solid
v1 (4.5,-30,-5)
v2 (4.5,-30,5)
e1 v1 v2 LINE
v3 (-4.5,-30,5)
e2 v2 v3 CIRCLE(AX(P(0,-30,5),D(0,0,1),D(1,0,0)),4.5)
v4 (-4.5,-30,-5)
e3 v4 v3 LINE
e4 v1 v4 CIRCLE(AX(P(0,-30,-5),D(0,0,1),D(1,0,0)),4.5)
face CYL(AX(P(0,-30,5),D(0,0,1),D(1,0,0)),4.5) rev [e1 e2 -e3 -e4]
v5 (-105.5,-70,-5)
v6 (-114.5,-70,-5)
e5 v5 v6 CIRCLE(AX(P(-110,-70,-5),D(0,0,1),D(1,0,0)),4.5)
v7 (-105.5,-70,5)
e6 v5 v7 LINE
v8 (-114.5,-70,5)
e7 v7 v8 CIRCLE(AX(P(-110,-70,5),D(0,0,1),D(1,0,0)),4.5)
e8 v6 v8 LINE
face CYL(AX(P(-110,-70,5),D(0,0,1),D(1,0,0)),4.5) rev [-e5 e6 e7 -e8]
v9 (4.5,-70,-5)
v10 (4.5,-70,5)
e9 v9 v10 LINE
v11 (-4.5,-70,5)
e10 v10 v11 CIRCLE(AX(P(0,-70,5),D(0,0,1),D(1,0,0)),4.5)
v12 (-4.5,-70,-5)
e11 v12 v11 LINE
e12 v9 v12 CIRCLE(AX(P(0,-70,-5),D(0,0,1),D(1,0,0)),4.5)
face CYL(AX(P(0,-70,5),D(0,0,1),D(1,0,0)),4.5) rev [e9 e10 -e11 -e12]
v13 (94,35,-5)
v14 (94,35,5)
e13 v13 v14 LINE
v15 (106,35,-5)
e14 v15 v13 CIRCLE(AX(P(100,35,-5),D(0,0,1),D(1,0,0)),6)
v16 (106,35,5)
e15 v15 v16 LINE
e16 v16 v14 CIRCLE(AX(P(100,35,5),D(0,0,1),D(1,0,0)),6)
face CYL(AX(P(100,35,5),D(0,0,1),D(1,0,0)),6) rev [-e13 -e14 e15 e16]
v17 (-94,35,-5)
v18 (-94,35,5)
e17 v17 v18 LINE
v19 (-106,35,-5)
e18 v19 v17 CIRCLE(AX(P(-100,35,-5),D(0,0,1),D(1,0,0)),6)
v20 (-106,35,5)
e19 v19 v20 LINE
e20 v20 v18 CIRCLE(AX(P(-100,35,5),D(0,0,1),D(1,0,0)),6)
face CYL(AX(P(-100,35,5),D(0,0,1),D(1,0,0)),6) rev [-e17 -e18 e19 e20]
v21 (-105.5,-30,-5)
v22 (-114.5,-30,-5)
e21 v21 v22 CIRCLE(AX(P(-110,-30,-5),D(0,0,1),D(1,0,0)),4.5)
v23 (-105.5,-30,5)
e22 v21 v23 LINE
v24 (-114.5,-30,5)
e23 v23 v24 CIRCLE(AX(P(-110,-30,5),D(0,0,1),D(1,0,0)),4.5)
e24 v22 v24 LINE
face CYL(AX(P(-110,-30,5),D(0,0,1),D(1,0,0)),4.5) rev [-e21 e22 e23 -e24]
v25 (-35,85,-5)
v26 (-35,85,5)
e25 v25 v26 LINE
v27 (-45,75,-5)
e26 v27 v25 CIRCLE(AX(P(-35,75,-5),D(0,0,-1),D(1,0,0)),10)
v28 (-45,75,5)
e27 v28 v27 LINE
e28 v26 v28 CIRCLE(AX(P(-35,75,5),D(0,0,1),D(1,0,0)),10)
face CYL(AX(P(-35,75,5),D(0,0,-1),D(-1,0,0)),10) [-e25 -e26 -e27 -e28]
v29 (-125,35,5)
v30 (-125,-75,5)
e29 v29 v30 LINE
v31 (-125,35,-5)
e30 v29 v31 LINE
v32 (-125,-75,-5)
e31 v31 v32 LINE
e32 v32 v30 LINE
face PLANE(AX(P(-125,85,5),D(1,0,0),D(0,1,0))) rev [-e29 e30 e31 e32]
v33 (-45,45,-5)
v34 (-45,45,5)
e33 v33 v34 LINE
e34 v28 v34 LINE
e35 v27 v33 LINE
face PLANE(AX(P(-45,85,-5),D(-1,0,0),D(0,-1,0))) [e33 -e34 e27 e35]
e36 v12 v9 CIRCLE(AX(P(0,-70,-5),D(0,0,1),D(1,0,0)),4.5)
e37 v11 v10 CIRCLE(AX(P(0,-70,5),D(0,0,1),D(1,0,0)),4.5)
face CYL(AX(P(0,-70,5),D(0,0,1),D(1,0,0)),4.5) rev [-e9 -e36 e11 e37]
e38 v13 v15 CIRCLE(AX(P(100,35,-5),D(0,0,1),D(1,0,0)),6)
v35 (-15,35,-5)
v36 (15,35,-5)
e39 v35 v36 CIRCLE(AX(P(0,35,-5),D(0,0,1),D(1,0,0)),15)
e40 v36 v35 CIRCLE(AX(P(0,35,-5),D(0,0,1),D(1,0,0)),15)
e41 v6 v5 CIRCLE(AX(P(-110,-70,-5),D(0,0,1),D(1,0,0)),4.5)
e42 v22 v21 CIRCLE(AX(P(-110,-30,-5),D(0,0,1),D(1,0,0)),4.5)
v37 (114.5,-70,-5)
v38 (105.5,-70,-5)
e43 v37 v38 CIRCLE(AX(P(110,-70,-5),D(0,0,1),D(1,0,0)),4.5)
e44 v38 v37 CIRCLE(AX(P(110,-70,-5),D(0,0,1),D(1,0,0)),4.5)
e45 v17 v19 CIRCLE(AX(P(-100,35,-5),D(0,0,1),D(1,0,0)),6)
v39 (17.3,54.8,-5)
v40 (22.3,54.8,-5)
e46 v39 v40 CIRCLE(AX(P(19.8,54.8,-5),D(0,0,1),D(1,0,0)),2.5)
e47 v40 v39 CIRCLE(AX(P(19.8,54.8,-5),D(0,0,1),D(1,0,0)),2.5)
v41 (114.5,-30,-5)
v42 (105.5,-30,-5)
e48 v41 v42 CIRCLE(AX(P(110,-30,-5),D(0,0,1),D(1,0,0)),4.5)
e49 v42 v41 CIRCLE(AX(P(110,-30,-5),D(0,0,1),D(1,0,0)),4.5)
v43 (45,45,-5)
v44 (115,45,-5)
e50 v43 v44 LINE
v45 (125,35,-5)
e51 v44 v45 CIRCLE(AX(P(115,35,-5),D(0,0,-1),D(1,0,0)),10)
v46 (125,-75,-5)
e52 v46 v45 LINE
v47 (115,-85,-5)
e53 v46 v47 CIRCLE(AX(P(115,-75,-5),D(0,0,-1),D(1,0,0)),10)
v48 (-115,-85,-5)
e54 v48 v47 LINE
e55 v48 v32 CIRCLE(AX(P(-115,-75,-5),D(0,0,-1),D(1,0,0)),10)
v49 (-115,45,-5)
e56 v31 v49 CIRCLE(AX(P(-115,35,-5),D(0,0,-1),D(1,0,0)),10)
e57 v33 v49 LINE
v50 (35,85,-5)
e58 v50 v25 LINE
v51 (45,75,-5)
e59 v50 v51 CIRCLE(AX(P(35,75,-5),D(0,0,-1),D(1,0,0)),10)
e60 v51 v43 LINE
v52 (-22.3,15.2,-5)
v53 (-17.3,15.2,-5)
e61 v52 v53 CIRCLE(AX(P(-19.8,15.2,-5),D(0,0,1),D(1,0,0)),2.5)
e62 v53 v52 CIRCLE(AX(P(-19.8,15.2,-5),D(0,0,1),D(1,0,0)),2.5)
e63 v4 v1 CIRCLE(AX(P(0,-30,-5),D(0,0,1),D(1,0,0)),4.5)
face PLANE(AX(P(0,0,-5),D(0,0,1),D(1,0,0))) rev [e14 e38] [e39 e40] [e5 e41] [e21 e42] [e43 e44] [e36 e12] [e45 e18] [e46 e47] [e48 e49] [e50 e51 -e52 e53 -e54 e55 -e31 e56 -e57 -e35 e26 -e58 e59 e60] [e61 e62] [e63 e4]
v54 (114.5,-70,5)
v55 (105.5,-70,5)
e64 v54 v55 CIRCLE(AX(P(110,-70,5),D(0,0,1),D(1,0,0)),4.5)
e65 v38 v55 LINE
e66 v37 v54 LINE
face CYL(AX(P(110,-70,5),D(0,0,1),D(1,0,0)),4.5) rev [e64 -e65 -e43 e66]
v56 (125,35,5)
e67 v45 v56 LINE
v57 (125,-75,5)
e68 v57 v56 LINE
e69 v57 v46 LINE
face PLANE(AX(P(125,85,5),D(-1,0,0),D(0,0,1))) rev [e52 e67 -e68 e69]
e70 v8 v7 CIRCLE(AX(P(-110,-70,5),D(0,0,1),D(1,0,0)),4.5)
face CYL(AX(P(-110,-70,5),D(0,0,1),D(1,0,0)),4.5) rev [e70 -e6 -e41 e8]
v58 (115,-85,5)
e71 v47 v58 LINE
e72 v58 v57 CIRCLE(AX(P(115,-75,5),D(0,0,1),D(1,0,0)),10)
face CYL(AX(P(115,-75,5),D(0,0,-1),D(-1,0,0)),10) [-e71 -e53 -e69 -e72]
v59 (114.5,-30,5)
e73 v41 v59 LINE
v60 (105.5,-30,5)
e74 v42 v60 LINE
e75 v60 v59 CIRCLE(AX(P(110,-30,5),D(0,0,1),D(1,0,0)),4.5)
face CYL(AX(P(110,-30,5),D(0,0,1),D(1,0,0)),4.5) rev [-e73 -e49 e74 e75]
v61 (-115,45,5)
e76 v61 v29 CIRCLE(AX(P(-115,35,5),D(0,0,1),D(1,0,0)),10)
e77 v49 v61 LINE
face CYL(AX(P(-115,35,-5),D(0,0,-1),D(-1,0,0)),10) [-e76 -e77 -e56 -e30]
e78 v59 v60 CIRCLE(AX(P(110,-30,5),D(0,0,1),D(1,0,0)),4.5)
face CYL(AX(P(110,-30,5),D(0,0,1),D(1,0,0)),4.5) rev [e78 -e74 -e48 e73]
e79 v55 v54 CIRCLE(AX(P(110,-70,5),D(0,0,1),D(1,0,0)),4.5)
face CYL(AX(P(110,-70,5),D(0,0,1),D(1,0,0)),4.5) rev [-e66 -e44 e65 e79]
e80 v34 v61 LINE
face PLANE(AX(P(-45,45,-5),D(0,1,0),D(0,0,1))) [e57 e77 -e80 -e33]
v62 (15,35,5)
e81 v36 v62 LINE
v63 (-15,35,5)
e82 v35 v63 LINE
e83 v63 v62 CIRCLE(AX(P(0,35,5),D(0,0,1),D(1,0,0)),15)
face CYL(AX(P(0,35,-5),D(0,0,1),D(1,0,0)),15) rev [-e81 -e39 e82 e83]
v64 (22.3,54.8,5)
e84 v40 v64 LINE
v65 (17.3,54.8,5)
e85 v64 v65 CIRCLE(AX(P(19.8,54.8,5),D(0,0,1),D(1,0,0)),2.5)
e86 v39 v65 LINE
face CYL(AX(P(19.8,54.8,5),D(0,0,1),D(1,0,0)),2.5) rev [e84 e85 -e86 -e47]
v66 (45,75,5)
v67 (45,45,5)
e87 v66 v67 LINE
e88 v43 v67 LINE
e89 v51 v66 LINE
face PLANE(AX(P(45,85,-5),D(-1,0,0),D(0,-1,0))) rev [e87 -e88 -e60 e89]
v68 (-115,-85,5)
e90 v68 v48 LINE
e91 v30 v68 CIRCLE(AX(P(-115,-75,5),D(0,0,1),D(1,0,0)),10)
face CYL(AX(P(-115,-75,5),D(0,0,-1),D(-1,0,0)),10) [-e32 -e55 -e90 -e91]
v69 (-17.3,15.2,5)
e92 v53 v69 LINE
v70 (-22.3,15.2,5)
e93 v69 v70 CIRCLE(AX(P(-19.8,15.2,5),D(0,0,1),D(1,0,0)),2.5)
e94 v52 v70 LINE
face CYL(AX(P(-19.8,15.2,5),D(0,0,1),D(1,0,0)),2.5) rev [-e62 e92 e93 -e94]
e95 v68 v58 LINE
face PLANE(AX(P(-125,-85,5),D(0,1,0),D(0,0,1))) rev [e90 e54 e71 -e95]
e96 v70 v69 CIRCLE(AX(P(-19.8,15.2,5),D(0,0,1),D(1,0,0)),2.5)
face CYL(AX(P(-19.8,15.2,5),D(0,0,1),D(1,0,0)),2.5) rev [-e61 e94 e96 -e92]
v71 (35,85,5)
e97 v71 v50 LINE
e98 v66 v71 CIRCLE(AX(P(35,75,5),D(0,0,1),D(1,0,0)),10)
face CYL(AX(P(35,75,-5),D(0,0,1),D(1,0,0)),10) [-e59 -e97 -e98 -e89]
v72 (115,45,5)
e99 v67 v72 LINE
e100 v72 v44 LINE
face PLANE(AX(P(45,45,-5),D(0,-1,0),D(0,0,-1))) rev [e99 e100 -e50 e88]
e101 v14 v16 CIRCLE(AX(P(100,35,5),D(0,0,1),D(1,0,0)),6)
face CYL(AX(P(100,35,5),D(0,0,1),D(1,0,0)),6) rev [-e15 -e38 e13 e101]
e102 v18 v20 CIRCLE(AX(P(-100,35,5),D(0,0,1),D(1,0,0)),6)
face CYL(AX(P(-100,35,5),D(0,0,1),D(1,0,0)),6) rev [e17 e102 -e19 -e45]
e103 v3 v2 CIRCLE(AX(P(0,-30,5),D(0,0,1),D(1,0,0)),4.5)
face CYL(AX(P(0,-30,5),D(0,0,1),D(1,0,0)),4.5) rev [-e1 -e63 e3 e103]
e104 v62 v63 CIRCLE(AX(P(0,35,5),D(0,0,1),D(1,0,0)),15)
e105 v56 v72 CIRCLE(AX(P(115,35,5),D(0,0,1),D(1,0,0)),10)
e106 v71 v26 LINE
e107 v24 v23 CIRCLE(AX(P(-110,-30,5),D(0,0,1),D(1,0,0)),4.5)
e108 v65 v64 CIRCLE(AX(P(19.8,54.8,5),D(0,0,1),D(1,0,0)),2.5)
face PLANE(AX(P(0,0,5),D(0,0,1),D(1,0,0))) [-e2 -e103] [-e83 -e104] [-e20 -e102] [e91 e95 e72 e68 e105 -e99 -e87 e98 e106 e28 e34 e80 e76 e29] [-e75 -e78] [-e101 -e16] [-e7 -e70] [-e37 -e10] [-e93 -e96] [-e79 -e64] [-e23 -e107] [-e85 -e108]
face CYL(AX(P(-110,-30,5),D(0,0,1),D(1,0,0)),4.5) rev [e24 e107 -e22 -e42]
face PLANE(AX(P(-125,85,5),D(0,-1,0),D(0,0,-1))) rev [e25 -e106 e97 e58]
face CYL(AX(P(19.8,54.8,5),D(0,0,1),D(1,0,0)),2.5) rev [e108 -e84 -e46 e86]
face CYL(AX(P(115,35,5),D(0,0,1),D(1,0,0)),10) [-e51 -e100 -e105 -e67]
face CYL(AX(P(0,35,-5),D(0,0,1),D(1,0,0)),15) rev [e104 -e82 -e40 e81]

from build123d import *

# Parameters (mm, degrees)
SKETCH_1_W              = 250
SKETCH_1_H              = 170
EXTRUDE_1_DEPTH         = 5
SKETCH_2_W              = 80
SKETCH_2_H              = 40
CUT_EXTRUDE_1_DEPTH     = 10
HOLE_WIZARD_9_0_9_1_D   = 9
PATTERN_LINEAR_1_COUNT  = 3
PATTERN_LINEAR_1_PITCH  = 110
HOLE_WIZARD_12_0_12_1_D = 12
SKETCH_7_R              = 15
CUT_EXTRUDE_2_DEPTH     = 10
HOLE_WIZARD_M6_1_D      = 5
FILLET_1_R              = 10


with BuildPart() as part:
    # 草图1 → 凸台-拉伸1 (new, symmetric)
    with BuildSketch(Plane.XY):
        Rectangle(SKETCH_1_W, SKETCH_1_H)
    extrude(amount=EXTRUDE_1_DEPTH, both=True)

    # 草图2 → 切除-拉伸1 (cut)
    with BuildSketch(Plane.XY.offset(5)):
        with Locations((85, 65)):
            Rectangle(SKETCH_2_W, SKETCH_2_H)
    cut_extrude_1 = extrude(amount=-CUT_EXTRUDE_1_DEPTH, mode=Mode.SUBTRACT)

    # 镜向1: 切除-拉伸1 across plane
    add(cut_extrude_1.mirror(Plane(origin=(0, 0, 0), x_dir=(0, 0, 1), z_dir=(1, 0, 0))), mode=Mode.SUBTRACT)

    # Ø9.0 (9) 直径孔1 (through all)
    with Locations(Plane.XY.offset(5)):
        with Locations((-110, -30), (-110, -70)):
            hole_wizard_9_0_9_1 = Hole(HOLE_WIZARD_9_0_9_1_D / 2)

    # 阵列(线性)1: Ø9.0 (9) 直径孔1 ×3
    with Locations(*[(i * PATTERN_LINEAR_1_PITCH, 0, 0) for i in range(1, PATTERN_LINEAR_1_COUNT)]):
        add(hole_wizard_9_0_9_1, mode=Mode.SUBTRACT)

    # Ø12.0 (12) 直径孔1 (through all)
    with Locations(Plane.XY.offset(5)):
        with Locations((-100, 35), (100, 35)):
            Hole(HOLE_WIZARD_12_0_12_1_D / 2)

    # 草图7 → 切除-拉伸2 (cut)
    with BuildSketch(Plane.XY.offset(5)):
        with Locations((0, 35)):
            Circle(SKETCH_7_R)
    extrude(amount=-CUT_EXTRUDE_2_DEPTH, mode=Mode.SUBTRACT)

    # M6 螺纹孔1 (through all)
    with Locations(Plane.XY.offset(5)):
        with Locations((-19.8, 15.2), (19.8, 54.8)):
            Hole(HOLE_WIZARD_M6_1_D / 2)

    # 圆角1
    fillet_1_edges = [part.edges().sort_by_distance(p)[0] for p in [
        (45, 85, 0),
        (125, 45, 0),
        (-45, 85, 0),
        (-125, 45, 0),
        (125, -85, 0),
        (-125, -85, 0),
    ]]
    fillet(fillet_1_edges, radius=FILLET_1_R)


solid = part.part
